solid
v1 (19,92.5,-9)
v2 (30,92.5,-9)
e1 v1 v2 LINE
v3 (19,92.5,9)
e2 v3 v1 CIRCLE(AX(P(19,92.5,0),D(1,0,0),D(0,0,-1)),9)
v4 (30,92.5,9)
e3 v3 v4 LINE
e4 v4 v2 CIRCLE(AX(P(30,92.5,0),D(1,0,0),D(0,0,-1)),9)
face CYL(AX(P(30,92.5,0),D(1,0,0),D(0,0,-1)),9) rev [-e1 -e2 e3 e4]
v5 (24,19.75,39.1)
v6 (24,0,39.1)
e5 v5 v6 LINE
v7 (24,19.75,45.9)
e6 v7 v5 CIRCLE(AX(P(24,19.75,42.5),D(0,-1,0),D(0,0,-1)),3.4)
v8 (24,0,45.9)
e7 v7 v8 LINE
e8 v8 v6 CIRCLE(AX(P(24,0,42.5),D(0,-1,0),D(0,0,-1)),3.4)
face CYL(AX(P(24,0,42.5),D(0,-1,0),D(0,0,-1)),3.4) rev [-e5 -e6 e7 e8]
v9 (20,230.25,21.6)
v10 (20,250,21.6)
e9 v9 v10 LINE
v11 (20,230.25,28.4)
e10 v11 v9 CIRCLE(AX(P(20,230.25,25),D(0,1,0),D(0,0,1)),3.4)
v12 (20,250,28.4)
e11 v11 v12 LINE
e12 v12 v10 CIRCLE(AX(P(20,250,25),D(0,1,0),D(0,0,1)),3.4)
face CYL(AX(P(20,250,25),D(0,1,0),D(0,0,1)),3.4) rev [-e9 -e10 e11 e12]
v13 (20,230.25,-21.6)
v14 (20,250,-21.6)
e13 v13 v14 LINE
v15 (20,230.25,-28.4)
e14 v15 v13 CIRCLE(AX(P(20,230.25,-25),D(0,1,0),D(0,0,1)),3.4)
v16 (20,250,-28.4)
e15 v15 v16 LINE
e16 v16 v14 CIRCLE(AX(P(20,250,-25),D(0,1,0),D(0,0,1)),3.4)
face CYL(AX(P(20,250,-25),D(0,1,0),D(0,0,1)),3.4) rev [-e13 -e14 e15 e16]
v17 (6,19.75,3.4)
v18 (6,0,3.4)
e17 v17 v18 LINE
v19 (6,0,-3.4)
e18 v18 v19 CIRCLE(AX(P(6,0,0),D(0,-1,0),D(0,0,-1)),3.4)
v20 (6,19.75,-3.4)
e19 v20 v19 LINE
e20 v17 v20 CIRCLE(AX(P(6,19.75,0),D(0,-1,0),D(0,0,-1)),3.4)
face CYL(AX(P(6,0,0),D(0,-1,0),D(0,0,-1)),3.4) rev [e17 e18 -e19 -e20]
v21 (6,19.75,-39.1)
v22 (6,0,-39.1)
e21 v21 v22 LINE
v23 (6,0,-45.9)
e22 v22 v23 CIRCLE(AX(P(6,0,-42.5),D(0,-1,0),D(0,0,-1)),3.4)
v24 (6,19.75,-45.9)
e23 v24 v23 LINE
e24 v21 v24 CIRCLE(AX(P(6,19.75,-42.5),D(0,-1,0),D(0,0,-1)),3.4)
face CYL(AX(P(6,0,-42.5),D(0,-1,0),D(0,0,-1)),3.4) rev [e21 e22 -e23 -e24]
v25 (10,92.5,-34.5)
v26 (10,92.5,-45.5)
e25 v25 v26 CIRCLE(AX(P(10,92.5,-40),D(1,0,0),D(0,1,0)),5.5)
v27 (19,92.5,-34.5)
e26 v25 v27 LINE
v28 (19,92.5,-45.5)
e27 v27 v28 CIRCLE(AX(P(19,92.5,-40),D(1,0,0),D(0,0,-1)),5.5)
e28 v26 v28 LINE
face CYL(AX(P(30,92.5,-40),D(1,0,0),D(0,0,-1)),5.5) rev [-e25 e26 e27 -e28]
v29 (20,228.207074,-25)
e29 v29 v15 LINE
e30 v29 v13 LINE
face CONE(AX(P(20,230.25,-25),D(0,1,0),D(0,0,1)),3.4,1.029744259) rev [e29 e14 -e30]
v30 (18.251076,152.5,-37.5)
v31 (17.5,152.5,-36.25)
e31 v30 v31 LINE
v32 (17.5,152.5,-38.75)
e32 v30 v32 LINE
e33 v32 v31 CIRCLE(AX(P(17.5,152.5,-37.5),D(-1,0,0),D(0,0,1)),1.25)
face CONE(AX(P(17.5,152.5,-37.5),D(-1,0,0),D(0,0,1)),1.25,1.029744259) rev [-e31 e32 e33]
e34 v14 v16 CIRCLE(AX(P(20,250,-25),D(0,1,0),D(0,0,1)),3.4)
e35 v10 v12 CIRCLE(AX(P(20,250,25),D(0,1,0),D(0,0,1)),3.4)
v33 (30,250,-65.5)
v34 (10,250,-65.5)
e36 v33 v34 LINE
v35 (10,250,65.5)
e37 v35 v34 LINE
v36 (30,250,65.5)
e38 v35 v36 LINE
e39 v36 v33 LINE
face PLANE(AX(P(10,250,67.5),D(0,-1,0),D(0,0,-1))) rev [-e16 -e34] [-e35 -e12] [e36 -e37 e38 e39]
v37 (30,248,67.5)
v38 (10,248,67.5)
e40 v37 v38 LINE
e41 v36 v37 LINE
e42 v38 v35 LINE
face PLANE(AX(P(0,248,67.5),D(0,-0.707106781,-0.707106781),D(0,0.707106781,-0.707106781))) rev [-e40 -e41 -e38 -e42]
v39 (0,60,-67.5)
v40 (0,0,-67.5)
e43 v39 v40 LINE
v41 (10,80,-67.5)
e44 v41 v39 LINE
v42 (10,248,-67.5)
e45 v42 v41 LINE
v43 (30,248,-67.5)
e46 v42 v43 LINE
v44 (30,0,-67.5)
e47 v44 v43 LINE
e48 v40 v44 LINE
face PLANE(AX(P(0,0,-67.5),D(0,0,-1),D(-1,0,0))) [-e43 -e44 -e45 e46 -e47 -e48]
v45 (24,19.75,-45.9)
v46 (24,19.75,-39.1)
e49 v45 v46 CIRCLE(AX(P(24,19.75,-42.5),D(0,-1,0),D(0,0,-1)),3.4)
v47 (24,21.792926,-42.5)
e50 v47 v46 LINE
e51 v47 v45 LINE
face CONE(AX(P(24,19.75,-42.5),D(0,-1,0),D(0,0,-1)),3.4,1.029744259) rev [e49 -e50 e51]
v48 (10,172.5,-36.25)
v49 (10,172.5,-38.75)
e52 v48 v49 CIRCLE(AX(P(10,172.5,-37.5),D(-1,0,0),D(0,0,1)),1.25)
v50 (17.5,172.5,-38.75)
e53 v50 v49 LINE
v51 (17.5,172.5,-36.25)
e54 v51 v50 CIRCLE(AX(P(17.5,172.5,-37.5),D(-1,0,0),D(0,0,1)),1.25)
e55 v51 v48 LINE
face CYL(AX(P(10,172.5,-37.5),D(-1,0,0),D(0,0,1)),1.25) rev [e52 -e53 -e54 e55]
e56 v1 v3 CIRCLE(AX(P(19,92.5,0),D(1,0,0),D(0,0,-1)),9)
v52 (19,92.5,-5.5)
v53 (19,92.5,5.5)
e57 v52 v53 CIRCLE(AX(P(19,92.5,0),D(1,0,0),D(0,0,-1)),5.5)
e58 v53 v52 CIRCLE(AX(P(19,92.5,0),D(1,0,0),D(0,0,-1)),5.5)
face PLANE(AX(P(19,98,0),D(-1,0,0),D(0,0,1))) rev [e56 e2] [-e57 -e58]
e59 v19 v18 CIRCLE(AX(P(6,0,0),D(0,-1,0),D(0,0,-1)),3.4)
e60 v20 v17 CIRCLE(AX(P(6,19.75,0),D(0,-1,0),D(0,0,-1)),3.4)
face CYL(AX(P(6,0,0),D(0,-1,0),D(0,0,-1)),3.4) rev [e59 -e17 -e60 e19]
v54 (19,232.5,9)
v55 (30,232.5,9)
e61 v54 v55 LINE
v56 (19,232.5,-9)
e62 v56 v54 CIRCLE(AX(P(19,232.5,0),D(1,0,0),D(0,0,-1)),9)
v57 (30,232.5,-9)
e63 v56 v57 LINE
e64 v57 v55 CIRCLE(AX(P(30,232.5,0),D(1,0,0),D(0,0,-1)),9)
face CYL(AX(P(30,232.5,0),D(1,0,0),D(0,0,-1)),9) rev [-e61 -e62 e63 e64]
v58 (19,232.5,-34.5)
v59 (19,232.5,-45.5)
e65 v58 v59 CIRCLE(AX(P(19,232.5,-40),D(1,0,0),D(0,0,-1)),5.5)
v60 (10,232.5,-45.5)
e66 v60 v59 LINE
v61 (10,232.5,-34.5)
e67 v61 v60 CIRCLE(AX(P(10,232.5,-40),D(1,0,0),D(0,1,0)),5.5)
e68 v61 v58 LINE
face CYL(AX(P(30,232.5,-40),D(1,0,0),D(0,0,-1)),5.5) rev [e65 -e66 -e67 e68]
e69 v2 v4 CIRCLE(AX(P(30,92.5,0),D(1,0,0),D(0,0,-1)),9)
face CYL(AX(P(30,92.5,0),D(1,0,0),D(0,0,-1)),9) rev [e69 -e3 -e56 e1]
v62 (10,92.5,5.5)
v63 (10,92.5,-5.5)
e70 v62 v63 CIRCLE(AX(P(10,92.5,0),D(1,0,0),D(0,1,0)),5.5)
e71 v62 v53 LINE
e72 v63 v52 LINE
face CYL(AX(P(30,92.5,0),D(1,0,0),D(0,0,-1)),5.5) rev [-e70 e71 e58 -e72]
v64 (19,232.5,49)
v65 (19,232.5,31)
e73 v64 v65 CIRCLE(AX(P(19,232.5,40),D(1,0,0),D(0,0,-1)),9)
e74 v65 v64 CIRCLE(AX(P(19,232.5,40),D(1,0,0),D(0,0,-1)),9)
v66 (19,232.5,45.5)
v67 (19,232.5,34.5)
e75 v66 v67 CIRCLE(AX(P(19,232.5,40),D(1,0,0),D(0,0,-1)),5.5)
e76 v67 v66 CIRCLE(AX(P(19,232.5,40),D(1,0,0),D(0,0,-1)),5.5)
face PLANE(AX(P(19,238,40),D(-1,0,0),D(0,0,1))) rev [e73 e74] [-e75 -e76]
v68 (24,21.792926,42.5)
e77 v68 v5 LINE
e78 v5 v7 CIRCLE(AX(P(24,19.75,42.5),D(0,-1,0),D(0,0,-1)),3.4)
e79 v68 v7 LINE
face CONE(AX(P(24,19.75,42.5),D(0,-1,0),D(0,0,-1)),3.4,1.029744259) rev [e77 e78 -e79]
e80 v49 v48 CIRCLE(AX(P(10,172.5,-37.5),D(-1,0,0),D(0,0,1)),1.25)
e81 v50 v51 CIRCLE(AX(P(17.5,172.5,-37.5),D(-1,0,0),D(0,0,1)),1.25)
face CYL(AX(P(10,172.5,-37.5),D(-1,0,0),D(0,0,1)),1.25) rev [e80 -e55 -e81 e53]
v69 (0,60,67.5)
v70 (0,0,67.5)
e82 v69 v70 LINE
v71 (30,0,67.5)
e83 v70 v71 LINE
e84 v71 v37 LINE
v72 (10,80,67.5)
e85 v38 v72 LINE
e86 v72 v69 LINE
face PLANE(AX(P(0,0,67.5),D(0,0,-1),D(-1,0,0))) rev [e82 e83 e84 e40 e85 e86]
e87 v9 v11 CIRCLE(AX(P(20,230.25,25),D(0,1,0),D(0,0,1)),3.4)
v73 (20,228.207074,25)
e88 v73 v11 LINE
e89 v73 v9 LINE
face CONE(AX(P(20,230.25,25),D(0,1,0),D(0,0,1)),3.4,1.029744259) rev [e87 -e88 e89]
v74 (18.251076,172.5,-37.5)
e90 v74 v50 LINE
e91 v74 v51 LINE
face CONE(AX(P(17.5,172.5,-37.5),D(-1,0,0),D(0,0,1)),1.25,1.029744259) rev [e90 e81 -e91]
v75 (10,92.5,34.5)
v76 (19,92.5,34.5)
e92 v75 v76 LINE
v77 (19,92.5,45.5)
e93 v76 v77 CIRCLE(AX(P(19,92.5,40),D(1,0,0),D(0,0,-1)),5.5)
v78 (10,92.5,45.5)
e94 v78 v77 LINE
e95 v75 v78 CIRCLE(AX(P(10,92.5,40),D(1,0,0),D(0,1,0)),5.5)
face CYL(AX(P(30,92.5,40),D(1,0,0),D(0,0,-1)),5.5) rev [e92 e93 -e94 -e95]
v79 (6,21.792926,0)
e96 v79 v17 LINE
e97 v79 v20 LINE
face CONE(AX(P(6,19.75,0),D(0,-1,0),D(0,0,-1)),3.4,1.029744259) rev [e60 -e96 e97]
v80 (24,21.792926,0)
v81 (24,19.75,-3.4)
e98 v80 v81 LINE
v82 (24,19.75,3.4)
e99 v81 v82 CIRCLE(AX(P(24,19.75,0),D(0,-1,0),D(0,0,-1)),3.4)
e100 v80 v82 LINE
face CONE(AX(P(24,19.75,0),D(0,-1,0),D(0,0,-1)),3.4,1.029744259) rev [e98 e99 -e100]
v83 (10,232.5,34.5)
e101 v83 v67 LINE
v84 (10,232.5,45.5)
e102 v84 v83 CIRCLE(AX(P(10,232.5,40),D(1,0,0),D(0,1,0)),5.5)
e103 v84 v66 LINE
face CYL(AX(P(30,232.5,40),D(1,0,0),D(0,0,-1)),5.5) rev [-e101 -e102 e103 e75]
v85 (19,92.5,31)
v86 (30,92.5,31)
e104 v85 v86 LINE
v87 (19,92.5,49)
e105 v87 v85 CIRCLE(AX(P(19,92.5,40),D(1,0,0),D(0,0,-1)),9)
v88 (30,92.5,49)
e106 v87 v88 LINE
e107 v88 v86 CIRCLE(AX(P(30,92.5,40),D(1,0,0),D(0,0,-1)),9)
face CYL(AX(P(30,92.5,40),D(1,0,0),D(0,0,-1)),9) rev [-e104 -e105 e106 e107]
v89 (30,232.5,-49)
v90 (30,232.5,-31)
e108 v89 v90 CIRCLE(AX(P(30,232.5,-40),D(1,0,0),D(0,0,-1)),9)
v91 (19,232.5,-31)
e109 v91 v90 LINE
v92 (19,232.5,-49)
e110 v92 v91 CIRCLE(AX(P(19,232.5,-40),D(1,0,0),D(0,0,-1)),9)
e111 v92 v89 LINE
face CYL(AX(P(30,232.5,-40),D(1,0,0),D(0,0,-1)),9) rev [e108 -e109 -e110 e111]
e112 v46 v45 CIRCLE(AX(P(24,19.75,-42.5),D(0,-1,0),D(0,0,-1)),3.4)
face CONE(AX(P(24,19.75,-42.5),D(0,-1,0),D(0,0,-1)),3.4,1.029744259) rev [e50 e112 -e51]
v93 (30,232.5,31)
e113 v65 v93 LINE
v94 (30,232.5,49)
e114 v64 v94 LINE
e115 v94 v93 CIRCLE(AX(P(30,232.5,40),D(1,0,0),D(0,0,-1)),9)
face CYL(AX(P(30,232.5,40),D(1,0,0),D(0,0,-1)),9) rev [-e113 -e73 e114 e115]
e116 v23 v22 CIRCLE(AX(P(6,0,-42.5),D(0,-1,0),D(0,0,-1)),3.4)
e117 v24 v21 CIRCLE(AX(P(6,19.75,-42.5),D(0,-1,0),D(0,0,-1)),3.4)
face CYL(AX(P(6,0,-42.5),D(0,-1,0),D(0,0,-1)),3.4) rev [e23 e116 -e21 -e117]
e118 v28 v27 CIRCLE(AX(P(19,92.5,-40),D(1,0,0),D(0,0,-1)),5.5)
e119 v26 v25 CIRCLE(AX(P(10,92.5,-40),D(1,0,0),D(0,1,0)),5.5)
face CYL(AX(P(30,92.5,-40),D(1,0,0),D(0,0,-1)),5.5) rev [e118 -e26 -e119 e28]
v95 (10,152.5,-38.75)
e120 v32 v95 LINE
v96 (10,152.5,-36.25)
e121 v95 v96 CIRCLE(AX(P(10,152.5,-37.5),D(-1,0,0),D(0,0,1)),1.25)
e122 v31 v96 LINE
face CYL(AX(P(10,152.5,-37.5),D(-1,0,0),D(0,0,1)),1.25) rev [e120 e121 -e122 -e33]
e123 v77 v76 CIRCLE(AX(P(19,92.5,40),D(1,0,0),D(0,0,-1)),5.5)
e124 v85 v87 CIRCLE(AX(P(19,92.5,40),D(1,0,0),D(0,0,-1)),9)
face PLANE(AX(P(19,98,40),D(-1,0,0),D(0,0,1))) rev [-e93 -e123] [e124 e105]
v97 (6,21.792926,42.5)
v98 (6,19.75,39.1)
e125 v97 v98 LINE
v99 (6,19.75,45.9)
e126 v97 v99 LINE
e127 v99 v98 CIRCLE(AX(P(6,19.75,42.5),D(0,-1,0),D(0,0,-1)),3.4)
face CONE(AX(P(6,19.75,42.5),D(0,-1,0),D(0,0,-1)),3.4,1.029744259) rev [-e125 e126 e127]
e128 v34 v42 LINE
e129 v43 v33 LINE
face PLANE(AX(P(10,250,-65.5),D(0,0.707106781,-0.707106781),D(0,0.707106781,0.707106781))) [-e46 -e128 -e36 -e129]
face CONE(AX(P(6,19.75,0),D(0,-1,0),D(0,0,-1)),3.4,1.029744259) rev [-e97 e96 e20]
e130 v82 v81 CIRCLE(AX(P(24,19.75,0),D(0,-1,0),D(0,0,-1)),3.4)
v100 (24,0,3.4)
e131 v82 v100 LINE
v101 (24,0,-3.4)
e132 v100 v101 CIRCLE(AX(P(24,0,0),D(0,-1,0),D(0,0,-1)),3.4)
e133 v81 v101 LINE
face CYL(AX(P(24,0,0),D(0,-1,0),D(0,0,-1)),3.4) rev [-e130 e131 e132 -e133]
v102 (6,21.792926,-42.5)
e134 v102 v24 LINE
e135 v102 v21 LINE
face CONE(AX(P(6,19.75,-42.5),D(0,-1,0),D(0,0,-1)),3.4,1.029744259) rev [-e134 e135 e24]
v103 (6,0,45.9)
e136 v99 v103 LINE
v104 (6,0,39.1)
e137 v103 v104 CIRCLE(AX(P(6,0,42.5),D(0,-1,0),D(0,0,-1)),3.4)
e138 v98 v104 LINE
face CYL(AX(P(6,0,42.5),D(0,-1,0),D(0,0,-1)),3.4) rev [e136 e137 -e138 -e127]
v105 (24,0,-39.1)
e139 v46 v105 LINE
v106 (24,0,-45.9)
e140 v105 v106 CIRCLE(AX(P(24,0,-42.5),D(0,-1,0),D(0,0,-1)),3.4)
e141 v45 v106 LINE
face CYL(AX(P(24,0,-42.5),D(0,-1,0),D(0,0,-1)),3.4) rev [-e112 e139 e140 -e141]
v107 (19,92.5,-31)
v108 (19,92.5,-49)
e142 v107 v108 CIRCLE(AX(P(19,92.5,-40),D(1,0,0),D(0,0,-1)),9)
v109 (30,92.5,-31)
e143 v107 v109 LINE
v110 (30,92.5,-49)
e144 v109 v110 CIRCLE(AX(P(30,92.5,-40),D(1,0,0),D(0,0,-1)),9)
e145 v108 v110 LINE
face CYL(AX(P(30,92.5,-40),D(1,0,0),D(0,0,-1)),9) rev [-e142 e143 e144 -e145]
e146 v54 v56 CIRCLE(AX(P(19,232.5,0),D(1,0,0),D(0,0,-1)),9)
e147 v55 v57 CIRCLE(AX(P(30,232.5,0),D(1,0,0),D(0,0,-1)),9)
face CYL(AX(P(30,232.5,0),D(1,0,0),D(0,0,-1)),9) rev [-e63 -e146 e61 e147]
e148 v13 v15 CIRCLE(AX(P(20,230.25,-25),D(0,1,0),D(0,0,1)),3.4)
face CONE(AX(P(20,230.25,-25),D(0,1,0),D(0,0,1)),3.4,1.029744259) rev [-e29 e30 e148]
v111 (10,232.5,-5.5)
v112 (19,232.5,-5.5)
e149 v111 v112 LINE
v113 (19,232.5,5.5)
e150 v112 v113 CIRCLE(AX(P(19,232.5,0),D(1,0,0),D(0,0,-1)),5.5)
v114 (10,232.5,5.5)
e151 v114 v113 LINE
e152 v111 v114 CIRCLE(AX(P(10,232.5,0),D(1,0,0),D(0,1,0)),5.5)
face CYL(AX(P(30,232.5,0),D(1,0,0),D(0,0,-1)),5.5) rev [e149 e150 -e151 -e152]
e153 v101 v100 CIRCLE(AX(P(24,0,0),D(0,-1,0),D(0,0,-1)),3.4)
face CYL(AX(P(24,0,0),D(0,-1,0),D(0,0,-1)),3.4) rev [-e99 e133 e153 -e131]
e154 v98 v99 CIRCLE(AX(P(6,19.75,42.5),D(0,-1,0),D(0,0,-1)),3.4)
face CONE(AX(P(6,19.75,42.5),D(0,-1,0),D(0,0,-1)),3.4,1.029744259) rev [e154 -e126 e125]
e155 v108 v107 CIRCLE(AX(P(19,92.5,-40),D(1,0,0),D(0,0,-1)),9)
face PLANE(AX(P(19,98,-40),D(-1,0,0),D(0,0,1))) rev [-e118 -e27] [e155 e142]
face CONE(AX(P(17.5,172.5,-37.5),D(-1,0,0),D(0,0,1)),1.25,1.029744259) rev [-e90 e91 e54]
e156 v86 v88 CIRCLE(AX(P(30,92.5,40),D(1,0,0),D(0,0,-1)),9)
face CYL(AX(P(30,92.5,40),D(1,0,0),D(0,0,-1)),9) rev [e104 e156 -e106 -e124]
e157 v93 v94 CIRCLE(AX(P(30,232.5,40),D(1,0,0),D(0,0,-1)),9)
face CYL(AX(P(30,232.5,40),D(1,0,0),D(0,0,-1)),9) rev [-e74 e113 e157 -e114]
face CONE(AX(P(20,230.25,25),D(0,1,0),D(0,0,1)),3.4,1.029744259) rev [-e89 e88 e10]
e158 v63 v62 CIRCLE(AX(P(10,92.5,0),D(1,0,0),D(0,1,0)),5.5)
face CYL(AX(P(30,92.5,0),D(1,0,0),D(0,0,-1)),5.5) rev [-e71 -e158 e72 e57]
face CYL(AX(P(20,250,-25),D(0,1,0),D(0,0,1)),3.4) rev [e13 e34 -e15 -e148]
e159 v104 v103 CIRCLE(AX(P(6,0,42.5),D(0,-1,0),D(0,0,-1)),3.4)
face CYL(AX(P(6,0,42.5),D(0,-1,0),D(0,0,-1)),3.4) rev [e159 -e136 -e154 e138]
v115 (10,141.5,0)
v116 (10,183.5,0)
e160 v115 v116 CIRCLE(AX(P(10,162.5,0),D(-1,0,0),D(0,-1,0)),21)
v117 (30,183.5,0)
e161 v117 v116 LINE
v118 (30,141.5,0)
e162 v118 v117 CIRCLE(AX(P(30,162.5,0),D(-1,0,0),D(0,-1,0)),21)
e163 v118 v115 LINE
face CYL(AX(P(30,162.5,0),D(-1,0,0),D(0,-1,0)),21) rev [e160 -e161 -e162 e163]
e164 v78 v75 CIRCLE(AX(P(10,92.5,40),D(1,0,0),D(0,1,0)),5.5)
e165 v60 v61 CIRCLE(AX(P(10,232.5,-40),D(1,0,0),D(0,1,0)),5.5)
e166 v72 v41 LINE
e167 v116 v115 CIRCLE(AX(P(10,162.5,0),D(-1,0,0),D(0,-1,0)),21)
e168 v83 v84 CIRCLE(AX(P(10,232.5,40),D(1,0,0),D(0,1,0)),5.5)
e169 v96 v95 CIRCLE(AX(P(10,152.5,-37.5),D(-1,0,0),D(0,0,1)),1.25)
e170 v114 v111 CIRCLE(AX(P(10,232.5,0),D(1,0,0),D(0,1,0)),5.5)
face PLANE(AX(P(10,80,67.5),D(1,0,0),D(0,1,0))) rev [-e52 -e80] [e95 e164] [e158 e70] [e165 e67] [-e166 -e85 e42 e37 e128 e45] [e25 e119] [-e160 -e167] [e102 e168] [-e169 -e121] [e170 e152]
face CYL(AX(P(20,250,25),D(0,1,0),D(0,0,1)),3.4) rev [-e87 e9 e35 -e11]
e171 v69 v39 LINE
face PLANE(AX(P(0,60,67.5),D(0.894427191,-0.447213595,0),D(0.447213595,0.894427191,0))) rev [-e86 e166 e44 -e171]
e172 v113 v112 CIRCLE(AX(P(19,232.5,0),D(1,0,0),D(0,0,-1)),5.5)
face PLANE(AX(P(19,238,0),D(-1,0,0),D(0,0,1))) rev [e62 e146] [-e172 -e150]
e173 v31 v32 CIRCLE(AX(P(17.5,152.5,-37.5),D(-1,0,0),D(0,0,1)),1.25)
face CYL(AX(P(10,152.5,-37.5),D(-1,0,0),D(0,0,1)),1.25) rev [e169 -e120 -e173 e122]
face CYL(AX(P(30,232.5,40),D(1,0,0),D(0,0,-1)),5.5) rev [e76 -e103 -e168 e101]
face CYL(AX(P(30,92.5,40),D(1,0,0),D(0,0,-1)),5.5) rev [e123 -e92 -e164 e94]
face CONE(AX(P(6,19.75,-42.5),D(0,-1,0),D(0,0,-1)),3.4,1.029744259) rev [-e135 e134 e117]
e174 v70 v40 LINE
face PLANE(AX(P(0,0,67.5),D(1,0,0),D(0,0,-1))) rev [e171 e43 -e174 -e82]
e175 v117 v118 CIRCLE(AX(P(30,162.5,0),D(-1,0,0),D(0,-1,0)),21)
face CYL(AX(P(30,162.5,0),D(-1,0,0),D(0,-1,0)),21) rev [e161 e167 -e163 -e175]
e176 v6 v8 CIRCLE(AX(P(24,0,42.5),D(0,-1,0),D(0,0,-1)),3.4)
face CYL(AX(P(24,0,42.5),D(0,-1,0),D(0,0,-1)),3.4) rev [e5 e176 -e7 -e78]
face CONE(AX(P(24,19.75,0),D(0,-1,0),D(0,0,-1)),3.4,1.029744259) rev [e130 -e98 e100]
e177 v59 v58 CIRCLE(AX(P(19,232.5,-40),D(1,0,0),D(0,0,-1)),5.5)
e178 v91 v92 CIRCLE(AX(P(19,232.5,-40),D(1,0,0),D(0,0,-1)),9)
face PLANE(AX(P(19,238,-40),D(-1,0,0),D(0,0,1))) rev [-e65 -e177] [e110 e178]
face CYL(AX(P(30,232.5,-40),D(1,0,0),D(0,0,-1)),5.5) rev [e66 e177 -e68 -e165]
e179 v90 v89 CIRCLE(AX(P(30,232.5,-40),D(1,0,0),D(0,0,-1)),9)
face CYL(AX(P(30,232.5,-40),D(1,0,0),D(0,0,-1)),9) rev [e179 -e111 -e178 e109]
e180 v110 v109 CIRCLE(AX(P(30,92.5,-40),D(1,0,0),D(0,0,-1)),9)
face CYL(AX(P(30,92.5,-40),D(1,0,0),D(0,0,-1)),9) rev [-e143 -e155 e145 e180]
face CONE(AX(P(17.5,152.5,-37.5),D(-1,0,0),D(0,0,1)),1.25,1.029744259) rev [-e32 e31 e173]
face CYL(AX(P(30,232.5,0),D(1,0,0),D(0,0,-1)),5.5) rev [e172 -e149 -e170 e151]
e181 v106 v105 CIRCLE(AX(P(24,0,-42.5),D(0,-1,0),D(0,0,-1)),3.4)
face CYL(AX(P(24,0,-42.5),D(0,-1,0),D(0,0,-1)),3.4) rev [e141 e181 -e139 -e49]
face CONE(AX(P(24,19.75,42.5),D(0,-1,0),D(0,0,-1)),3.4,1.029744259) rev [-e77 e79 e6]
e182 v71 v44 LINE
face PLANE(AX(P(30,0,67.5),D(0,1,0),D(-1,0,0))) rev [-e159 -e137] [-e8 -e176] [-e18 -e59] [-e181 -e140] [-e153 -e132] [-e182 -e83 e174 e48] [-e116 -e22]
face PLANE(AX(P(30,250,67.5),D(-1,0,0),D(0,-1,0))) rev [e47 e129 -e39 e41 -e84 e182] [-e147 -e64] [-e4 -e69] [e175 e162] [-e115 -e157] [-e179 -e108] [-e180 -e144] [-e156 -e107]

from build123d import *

# Parameters (mm, degrees)
BOSS_EXTRUDE1_DEPTH                                  = 67.5
M8_TAPPED_HOLE1_D                                    = 6.8
M8_TAPPED_HOLE1_DEPTH                                = 19.75
M8_TAPPED_HOLE1_TIP                                  = 2.042926105
HOLE_SIZE_PER_SOCKET_HEAD_CAP_SCREW_TYPE_D           = 11
HOLE_SIZE_PER_SOCKET_HEAD_CAP_SCREW_TYPE_CBORE_D     = 18
HOLE_SIZE_PER_SOCKET_HEAD_CAP_SCREW_TYPE_CBORE_DEPTH = 11
SKETCH8_R                                            = 21
CUT_EXTRUDE1_DEPTH                                   = 260.723410574
M8_TAPPED_HOLE2_D                                    = 6.8
M8_TAPPED_HOLE2_DEPTH                                = 19.75
M8_TAPPED_HOLE2_TIP                                  = 2.042926105
CHAMFER1_SIZE                                        = 2
M3_TAPPED_HOLE1_D                                    = 2.5
M3_TAPPED_HOLE1_DEPTH                                = 7.5
M3_TAPPED_HOLE1_TIP                                  = 0.751075774


with BuildPart() as part:
    # Sketch1 → Boss-Extrude1 (new, symmetric)
    with BuildSketch(Plane.XY):
        Polygon((0, 0), (0, 60), (10, 80), (10, 250), (30, 250), (30, 0), align=None)
    extrude(amount=BOSS_EXTRUDE1_DEPTH, both=True)

    # M8 Tapped Hole1
    with Locations(Plane.XZ):
        with Locations((6, -42.5), (24, -42.5), (24, 0), (6, 0), (6, 42.5), (24, 42.5)):
            Hole(M8_TAPPED_HOLE1_D / 2, depth=M8_TAPPED_HOLE1_DEPTH)
            with Locations((0, 0, -(M8_TAPPED_HOLE1_DEPTH + M8_TAPPED_HOLE1_TIP / 2))):  # 118° drill point
                Cone(0, M8_TAPPED_HOLE1_D / 2, M8_TAPPED_HOLE1_TIP, mode=Mode.SUBTRACT)

    # Hole size per socket head cap screw type1 (through all)
    with Locations(Plane(origin=(30, 0, 0), x_dir=(0, 0, -1), z_dir=(1, 0, 0))):
        with Locations((-40, 232.5), (40, 232.5), (40, 92.5), (-40, 92.5), (0, 232.5), (0, 92.5)):
            CounterBoreHole(HOLE_SIZE_PER_SOCKET_HEAD_CAP_SCREW_TYPE_D / 2, HOLE_SIZE_PER_SOCKET_HEAD_CAP_SCREW_TYPE_CBORE_D / 2, HOLE_SIZE_PER_SOCKET_HEAD_CAP_SCREW_TYPE_CBORE_DEPTH)

    # Sketch8 → Cut-Extrude1 (cut, through all)
    with BuildSketch(Plane.ZY.offset(-10)):
        with Locations(Location((0, 162.5, 0), (0, 0, 270))):
            Circle(SKETCH8_R)
    extrude(amount=-CUT_EXTRUDE1_DEPTH, mode=Mode.SUBTRACT)

    # M8 Tapped Hole2
    with Locations(Plane(origin=(0, 250, 0), x_dir=(-1, 0, 0), z_dir=(0, 1, 0))):
        with Locations((-20, -25), (-20, 25)):
            Hole(M8_TAPPED_HOLE2_D / 2, depth=M8_TAPPED_HOLE2_DEPTH)
            with Locations((0, 0, -(M8_TAPPED_HOLE2_DEPTH + M8_TAPPED_HOLE2_TIP / 2))):  # 118° drill point
                Cone(0, M8_TAPPED_HOLE2_D / 2, M8_TAPPED_HOLE2_TIP, mode=Mode.SUBTRACT)

    # Chamfer1
    chamfer1_edges = [part.edges().sort_by_distance(p)[0] for p in [
        (20, 250, 67.5),
        (20, 250, -67.5),
    ]]
    chamfer(chamfer1_edges, length=CHAMFER1_SIZE)

    # M3 Tapped Hole1
    with Locations(Plane.ZY.offset(-10)):
        with Locations((-37.5, 152.5), (-37.5, 172.5)):
            Hole(M3_TAPPED_HOLE1_D / 2, depth=M3_TAPPED_HOLE1_DEPTH)
            with Locations((0, 0, -(M3_TAPPED_HOLE1_DEPTH + M3_TAPPED_HOLE1_TIP / 2))):  # 118° drill point
                Cone(0, M3_TAPPED_HOLE1_D / 2, M3_TAPPED_HOLE1_TIP, mode=Mode.SUBTRACT)


solid = part.part
